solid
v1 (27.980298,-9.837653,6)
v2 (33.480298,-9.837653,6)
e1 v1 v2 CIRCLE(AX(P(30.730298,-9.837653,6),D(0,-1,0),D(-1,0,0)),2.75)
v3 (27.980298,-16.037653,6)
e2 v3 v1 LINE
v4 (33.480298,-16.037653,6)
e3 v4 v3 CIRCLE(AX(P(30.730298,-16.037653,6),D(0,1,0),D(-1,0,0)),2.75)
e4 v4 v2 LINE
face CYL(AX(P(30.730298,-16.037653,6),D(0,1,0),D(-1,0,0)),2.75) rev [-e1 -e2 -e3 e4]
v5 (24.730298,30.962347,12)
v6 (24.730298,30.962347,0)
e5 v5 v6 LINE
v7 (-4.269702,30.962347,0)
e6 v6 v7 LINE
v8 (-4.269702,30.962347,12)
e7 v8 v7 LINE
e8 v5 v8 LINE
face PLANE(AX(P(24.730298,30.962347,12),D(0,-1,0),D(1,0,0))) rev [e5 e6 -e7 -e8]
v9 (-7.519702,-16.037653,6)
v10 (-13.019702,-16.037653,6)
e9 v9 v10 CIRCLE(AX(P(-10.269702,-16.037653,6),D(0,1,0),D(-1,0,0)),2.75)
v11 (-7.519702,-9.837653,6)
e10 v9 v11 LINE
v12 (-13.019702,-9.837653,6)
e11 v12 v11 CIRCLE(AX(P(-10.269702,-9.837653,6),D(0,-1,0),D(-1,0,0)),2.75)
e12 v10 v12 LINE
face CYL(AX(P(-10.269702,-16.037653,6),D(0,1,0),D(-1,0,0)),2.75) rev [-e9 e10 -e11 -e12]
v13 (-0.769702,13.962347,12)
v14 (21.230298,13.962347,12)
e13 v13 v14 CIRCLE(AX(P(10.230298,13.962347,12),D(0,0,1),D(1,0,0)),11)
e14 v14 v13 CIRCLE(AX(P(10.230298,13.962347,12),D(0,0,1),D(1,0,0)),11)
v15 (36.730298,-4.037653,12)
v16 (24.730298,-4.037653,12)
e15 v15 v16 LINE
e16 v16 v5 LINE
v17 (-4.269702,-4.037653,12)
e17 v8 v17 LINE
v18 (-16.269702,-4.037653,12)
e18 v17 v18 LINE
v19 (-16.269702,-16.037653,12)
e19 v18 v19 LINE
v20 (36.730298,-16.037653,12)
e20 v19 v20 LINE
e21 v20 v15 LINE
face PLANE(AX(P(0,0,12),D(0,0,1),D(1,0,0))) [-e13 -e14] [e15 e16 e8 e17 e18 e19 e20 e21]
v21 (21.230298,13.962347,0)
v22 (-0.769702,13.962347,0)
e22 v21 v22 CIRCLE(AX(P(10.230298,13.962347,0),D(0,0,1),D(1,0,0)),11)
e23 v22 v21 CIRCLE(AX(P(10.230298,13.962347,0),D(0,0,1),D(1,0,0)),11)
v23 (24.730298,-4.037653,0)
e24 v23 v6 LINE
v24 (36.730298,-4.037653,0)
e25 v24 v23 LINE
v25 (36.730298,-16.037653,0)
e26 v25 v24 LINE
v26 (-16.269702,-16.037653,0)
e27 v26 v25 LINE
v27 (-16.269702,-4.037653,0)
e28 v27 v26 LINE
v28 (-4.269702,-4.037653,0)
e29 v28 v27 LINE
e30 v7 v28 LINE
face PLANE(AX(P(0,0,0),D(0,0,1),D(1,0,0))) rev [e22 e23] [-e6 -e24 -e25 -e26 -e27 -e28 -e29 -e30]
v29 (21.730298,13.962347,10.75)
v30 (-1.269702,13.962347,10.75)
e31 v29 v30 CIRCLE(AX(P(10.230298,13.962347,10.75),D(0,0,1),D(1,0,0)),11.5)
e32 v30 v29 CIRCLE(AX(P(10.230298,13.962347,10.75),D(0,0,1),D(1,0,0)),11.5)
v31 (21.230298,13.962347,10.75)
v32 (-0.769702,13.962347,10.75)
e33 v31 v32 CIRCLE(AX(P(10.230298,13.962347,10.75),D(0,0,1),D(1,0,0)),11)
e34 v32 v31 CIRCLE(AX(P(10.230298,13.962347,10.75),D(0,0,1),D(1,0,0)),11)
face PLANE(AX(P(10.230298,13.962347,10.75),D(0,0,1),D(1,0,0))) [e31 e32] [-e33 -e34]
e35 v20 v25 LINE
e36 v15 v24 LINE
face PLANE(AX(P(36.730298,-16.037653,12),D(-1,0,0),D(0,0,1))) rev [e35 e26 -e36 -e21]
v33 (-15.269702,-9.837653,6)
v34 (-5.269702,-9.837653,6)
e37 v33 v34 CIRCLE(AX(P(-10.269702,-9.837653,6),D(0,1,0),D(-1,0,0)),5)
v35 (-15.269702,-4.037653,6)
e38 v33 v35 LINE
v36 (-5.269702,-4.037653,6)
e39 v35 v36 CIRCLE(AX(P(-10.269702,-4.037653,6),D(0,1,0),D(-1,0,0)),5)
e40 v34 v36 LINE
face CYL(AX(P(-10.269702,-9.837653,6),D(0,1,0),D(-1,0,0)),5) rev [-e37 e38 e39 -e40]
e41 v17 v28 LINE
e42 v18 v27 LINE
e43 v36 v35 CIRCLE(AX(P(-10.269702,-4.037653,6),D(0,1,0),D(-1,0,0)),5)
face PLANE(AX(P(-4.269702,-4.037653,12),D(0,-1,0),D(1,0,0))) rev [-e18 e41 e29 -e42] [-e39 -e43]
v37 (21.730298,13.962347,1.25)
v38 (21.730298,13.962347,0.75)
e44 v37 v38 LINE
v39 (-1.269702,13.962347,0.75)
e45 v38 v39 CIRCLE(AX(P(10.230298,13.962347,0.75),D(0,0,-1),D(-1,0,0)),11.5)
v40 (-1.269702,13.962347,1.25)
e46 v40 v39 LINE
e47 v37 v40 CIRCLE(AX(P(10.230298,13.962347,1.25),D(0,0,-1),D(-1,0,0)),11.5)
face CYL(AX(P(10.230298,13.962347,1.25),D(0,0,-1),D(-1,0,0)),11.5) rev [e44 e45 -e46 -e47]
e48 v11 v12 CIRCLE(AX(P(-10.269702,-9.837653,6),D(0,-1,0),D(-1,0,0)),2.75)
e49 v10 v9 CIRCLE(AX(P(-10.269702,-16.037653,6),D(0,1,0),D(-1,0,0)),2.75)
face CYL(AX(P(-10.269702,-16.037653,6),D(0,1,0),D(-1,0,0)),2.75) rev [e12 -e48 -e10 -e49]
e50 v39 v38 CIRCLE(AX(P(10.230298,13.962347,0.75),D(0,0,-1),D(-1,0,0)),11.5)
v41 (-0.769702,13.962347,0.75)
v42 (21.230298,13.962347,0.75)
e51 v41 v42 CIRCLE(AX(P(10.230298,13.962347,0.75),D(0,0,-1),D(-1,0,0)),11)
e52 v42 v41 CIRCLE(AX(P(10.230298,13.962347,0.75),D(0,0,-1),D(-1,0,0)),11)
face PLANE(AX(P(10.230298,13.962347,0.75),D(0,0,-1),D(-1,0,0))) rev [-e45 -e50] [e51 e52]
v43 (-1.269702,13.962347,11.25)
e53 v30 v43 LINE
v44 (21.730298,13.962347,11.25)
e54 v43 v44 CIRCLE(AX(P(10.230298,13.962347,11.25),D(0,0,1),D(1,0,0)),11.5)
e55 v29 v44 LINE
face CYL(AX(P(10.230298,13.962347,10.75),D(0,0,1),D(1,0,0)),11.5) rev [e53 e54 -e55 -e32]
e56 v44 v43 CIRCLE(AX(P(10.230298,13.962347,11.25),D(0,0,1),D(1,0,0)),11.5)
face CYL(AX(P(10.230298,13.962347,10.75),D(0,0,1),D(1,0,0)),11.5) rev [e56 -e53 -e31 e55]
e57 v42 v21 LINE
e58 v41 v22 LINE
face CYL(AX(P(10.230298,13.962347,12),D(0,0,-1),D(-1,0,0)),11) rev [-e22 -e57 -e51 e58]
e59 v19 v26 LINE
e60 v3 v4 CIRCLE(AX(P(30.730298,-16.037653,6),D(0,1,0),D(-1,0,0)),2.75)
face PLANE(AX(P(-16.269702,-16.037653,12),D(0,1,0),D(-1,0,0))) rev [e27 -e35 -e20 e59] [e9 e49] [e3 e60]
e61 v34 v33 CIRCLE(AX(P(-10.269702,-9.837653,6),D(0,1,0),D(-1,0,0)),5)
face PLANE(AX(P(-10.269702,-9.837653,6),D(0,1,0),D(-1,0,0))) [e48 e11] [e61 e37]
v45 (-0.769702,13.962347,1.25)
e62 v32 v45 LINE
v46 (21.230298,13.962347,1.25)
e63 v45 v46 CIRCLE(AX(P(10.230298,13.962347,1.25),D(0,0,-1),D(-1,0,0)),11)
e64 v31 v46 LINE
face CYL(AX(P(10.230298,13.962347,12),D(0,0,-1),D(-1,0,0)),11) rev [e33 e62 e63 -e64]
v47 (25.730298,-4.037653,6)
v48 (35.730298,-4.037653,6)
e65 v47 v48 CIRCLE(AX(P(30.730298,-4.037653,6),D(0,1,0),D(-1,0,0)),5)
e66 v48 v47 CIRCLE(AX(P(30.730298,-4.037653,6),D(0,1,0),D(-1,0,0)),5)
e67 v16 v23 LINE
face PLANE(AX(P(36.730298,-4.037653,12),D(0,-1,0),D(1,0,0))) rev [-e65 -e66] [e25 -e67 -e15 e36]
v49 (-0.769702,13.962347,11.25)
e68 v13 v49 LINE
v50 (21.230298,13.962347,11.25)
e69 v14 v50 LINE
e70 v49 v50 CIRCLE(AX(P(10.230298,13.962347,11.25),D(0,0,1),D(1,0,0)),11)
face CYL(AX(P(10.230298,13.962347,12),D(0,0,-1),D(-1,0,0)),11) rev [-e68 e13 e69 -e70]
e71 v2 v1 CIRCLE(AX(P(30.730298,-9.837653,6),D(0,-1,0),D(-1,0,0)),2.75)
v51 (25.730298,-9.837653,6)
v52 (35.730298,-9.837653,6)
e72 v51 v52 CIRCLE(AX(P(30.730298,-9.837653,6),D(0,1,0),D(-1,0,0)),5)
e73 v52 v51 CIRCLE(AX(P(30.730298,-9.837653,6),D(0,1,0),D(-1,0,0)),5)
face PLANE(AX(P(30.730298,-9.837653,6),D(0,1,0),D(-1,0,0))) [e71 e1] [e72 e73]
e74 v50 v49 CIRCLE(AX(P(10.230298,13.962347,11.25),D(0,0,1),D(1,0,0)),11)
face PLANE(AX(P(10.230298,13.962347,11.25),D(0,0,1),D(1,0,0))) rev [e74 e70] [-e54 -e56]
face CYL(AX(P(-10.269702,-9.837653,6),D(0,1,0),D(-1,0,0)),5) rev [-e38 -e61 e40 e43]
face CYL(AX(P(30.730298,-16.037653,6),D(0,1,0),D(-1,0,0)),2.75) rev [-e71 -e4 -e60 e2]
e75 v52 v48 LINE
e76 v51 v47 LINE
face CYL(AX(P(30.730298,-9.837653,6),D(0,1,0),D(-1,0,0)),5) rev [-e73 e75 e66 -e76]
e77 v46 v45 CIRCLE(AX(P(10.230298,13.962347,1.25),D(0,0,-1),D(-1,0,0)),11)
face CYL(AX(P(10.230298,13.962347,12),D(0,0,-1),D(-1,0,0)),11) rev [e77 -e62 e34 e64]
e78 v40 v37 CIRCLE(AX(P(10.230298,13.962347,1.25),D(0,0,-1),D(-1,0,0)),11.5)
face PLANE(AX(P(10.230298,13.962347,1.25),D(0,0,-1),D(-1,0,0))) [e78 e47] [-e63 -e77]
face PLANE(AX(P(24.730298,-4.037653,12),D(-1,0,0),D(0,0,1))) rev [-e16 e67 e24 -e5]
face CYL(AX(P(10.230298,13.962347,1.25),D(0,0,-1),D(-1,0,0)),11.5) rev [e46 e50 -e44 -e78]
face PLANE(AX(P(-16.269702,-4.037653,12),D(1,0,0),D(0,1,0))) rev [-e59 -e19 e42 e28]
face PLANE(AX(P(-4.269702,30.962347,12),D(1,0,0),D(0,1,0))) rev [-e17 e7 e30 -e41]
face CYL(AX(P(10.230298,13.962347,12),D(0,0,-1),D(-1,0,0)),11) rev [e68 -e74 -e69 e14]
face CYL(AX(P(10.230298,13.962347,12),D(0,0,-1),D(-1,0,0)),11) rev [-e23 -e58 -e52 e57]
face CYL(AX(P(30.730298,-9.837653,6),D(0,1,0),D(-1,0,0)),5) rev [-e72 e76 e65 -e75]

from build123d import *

# Parameters (mm, degrees)
SKETCH_1_R          = 11
EXTRUDE_1_DEPTH     = 12
SKETCH_2_R          = 2.75
CUT_EXTRUDE_1_DEPTH = 53.135542299
SKETCH_3_R          = 5
CUT_EXTRUDE_2_DEPTH = 5.8
SKETCH_4_R          = 11.5
CUT_EXTRUDE_3_DEPTH = 0.25
SKETCH_5_R          = 11.5
CUT_EXTRUDE_4_DEPTH = 0.25


with BuildPart() as part:
    # 草图1 → 凸台-拉伸1 (new body)
    with BuildSketch(Plane.XY):
        Polygon((-16.269702277, -16.03765324), (36.730297723, -16.03765324), (36.730297723, -4.03765324), (24.730297723, -4.03765324), (24.730297723, 30.96234676), (-4.269702277, 30.96234676), (-4.269702277, -4.03765324), (-16.269702277, -4.03765324), align=None)
        with Locations((10.230297723, 13.96234676)):
            Circle(SKETCH_1_R, mode=Mode.SUBTRACT)
    extrude(amount=EXTRUDE_1_DEPTH)

    # 草图2 → 切除-拉伸1 (cut, through all)
    with BuildSketch(Plane(origin=(0, -4.03765324, 0), x_dir=(1, 0, 0), z_dir=(0, 1, 0))):
        with Locations(Location((-10.269702277, -6, 0), (0, 0, 180))):
            Circle(SKETCH_2_R)
        with Locations(Location((30.730297723, -6, 0), (0, 0, 180))):
            Circle(SKETCH_2_R)
    extrude(amount=-CUT_EXTRUDE_1_DEPTH, mode=Mode.SUBTRACT)

    # 草图3 → 切除-拉伸2 (cut)
    with BuildSketch(Plane(origin=(0, -4.03765324, 0), x_dir=(1, 0, 0), z_dir=(0, 1, 0))):
        with Locations(Location((-10.269702277, -6, 0), (0, 0, 180))):
            Circle(SKETCH_3_R)
        with Locations(Location((30.730297723, -6, 0), (0, 0, 180))):
            Circle(SKETCH_3_R)
    extrude(amount=-CUT_EXTRUDE_2_DEPTH, mode=Mode.SUBTRACT)

    # 草图4 → 切除-拉伸3 (cut, symmetric)
    with BuildSketch(Plane.XY.offset(11)):
        with Locations((10.230297723, 13.96234676)):
            Circle(SKETCH_4_R)
    extrude(amount=CUT_EXTRUDE_3_DEPTH, both=True, mode=Mode.SUBTRACT)

    # 草图5 → 切除-拉伸4 (cut, symmetric)
    with BuildSketch(Plane(origin=(0, 0, 1), x_dir=(-1, 0, 0), z_dir=(0, 0, -1))):
        with Locations(Location((-10.230297723, 13.96234676, 0), (0, 0, 180))):
            Circle(SKETCH_5_R)
    extrude(amount=CUT_EXTRUDE_4_DEPTH, both=True, mode=Mode.SUBTRACT)


solid = part.part
